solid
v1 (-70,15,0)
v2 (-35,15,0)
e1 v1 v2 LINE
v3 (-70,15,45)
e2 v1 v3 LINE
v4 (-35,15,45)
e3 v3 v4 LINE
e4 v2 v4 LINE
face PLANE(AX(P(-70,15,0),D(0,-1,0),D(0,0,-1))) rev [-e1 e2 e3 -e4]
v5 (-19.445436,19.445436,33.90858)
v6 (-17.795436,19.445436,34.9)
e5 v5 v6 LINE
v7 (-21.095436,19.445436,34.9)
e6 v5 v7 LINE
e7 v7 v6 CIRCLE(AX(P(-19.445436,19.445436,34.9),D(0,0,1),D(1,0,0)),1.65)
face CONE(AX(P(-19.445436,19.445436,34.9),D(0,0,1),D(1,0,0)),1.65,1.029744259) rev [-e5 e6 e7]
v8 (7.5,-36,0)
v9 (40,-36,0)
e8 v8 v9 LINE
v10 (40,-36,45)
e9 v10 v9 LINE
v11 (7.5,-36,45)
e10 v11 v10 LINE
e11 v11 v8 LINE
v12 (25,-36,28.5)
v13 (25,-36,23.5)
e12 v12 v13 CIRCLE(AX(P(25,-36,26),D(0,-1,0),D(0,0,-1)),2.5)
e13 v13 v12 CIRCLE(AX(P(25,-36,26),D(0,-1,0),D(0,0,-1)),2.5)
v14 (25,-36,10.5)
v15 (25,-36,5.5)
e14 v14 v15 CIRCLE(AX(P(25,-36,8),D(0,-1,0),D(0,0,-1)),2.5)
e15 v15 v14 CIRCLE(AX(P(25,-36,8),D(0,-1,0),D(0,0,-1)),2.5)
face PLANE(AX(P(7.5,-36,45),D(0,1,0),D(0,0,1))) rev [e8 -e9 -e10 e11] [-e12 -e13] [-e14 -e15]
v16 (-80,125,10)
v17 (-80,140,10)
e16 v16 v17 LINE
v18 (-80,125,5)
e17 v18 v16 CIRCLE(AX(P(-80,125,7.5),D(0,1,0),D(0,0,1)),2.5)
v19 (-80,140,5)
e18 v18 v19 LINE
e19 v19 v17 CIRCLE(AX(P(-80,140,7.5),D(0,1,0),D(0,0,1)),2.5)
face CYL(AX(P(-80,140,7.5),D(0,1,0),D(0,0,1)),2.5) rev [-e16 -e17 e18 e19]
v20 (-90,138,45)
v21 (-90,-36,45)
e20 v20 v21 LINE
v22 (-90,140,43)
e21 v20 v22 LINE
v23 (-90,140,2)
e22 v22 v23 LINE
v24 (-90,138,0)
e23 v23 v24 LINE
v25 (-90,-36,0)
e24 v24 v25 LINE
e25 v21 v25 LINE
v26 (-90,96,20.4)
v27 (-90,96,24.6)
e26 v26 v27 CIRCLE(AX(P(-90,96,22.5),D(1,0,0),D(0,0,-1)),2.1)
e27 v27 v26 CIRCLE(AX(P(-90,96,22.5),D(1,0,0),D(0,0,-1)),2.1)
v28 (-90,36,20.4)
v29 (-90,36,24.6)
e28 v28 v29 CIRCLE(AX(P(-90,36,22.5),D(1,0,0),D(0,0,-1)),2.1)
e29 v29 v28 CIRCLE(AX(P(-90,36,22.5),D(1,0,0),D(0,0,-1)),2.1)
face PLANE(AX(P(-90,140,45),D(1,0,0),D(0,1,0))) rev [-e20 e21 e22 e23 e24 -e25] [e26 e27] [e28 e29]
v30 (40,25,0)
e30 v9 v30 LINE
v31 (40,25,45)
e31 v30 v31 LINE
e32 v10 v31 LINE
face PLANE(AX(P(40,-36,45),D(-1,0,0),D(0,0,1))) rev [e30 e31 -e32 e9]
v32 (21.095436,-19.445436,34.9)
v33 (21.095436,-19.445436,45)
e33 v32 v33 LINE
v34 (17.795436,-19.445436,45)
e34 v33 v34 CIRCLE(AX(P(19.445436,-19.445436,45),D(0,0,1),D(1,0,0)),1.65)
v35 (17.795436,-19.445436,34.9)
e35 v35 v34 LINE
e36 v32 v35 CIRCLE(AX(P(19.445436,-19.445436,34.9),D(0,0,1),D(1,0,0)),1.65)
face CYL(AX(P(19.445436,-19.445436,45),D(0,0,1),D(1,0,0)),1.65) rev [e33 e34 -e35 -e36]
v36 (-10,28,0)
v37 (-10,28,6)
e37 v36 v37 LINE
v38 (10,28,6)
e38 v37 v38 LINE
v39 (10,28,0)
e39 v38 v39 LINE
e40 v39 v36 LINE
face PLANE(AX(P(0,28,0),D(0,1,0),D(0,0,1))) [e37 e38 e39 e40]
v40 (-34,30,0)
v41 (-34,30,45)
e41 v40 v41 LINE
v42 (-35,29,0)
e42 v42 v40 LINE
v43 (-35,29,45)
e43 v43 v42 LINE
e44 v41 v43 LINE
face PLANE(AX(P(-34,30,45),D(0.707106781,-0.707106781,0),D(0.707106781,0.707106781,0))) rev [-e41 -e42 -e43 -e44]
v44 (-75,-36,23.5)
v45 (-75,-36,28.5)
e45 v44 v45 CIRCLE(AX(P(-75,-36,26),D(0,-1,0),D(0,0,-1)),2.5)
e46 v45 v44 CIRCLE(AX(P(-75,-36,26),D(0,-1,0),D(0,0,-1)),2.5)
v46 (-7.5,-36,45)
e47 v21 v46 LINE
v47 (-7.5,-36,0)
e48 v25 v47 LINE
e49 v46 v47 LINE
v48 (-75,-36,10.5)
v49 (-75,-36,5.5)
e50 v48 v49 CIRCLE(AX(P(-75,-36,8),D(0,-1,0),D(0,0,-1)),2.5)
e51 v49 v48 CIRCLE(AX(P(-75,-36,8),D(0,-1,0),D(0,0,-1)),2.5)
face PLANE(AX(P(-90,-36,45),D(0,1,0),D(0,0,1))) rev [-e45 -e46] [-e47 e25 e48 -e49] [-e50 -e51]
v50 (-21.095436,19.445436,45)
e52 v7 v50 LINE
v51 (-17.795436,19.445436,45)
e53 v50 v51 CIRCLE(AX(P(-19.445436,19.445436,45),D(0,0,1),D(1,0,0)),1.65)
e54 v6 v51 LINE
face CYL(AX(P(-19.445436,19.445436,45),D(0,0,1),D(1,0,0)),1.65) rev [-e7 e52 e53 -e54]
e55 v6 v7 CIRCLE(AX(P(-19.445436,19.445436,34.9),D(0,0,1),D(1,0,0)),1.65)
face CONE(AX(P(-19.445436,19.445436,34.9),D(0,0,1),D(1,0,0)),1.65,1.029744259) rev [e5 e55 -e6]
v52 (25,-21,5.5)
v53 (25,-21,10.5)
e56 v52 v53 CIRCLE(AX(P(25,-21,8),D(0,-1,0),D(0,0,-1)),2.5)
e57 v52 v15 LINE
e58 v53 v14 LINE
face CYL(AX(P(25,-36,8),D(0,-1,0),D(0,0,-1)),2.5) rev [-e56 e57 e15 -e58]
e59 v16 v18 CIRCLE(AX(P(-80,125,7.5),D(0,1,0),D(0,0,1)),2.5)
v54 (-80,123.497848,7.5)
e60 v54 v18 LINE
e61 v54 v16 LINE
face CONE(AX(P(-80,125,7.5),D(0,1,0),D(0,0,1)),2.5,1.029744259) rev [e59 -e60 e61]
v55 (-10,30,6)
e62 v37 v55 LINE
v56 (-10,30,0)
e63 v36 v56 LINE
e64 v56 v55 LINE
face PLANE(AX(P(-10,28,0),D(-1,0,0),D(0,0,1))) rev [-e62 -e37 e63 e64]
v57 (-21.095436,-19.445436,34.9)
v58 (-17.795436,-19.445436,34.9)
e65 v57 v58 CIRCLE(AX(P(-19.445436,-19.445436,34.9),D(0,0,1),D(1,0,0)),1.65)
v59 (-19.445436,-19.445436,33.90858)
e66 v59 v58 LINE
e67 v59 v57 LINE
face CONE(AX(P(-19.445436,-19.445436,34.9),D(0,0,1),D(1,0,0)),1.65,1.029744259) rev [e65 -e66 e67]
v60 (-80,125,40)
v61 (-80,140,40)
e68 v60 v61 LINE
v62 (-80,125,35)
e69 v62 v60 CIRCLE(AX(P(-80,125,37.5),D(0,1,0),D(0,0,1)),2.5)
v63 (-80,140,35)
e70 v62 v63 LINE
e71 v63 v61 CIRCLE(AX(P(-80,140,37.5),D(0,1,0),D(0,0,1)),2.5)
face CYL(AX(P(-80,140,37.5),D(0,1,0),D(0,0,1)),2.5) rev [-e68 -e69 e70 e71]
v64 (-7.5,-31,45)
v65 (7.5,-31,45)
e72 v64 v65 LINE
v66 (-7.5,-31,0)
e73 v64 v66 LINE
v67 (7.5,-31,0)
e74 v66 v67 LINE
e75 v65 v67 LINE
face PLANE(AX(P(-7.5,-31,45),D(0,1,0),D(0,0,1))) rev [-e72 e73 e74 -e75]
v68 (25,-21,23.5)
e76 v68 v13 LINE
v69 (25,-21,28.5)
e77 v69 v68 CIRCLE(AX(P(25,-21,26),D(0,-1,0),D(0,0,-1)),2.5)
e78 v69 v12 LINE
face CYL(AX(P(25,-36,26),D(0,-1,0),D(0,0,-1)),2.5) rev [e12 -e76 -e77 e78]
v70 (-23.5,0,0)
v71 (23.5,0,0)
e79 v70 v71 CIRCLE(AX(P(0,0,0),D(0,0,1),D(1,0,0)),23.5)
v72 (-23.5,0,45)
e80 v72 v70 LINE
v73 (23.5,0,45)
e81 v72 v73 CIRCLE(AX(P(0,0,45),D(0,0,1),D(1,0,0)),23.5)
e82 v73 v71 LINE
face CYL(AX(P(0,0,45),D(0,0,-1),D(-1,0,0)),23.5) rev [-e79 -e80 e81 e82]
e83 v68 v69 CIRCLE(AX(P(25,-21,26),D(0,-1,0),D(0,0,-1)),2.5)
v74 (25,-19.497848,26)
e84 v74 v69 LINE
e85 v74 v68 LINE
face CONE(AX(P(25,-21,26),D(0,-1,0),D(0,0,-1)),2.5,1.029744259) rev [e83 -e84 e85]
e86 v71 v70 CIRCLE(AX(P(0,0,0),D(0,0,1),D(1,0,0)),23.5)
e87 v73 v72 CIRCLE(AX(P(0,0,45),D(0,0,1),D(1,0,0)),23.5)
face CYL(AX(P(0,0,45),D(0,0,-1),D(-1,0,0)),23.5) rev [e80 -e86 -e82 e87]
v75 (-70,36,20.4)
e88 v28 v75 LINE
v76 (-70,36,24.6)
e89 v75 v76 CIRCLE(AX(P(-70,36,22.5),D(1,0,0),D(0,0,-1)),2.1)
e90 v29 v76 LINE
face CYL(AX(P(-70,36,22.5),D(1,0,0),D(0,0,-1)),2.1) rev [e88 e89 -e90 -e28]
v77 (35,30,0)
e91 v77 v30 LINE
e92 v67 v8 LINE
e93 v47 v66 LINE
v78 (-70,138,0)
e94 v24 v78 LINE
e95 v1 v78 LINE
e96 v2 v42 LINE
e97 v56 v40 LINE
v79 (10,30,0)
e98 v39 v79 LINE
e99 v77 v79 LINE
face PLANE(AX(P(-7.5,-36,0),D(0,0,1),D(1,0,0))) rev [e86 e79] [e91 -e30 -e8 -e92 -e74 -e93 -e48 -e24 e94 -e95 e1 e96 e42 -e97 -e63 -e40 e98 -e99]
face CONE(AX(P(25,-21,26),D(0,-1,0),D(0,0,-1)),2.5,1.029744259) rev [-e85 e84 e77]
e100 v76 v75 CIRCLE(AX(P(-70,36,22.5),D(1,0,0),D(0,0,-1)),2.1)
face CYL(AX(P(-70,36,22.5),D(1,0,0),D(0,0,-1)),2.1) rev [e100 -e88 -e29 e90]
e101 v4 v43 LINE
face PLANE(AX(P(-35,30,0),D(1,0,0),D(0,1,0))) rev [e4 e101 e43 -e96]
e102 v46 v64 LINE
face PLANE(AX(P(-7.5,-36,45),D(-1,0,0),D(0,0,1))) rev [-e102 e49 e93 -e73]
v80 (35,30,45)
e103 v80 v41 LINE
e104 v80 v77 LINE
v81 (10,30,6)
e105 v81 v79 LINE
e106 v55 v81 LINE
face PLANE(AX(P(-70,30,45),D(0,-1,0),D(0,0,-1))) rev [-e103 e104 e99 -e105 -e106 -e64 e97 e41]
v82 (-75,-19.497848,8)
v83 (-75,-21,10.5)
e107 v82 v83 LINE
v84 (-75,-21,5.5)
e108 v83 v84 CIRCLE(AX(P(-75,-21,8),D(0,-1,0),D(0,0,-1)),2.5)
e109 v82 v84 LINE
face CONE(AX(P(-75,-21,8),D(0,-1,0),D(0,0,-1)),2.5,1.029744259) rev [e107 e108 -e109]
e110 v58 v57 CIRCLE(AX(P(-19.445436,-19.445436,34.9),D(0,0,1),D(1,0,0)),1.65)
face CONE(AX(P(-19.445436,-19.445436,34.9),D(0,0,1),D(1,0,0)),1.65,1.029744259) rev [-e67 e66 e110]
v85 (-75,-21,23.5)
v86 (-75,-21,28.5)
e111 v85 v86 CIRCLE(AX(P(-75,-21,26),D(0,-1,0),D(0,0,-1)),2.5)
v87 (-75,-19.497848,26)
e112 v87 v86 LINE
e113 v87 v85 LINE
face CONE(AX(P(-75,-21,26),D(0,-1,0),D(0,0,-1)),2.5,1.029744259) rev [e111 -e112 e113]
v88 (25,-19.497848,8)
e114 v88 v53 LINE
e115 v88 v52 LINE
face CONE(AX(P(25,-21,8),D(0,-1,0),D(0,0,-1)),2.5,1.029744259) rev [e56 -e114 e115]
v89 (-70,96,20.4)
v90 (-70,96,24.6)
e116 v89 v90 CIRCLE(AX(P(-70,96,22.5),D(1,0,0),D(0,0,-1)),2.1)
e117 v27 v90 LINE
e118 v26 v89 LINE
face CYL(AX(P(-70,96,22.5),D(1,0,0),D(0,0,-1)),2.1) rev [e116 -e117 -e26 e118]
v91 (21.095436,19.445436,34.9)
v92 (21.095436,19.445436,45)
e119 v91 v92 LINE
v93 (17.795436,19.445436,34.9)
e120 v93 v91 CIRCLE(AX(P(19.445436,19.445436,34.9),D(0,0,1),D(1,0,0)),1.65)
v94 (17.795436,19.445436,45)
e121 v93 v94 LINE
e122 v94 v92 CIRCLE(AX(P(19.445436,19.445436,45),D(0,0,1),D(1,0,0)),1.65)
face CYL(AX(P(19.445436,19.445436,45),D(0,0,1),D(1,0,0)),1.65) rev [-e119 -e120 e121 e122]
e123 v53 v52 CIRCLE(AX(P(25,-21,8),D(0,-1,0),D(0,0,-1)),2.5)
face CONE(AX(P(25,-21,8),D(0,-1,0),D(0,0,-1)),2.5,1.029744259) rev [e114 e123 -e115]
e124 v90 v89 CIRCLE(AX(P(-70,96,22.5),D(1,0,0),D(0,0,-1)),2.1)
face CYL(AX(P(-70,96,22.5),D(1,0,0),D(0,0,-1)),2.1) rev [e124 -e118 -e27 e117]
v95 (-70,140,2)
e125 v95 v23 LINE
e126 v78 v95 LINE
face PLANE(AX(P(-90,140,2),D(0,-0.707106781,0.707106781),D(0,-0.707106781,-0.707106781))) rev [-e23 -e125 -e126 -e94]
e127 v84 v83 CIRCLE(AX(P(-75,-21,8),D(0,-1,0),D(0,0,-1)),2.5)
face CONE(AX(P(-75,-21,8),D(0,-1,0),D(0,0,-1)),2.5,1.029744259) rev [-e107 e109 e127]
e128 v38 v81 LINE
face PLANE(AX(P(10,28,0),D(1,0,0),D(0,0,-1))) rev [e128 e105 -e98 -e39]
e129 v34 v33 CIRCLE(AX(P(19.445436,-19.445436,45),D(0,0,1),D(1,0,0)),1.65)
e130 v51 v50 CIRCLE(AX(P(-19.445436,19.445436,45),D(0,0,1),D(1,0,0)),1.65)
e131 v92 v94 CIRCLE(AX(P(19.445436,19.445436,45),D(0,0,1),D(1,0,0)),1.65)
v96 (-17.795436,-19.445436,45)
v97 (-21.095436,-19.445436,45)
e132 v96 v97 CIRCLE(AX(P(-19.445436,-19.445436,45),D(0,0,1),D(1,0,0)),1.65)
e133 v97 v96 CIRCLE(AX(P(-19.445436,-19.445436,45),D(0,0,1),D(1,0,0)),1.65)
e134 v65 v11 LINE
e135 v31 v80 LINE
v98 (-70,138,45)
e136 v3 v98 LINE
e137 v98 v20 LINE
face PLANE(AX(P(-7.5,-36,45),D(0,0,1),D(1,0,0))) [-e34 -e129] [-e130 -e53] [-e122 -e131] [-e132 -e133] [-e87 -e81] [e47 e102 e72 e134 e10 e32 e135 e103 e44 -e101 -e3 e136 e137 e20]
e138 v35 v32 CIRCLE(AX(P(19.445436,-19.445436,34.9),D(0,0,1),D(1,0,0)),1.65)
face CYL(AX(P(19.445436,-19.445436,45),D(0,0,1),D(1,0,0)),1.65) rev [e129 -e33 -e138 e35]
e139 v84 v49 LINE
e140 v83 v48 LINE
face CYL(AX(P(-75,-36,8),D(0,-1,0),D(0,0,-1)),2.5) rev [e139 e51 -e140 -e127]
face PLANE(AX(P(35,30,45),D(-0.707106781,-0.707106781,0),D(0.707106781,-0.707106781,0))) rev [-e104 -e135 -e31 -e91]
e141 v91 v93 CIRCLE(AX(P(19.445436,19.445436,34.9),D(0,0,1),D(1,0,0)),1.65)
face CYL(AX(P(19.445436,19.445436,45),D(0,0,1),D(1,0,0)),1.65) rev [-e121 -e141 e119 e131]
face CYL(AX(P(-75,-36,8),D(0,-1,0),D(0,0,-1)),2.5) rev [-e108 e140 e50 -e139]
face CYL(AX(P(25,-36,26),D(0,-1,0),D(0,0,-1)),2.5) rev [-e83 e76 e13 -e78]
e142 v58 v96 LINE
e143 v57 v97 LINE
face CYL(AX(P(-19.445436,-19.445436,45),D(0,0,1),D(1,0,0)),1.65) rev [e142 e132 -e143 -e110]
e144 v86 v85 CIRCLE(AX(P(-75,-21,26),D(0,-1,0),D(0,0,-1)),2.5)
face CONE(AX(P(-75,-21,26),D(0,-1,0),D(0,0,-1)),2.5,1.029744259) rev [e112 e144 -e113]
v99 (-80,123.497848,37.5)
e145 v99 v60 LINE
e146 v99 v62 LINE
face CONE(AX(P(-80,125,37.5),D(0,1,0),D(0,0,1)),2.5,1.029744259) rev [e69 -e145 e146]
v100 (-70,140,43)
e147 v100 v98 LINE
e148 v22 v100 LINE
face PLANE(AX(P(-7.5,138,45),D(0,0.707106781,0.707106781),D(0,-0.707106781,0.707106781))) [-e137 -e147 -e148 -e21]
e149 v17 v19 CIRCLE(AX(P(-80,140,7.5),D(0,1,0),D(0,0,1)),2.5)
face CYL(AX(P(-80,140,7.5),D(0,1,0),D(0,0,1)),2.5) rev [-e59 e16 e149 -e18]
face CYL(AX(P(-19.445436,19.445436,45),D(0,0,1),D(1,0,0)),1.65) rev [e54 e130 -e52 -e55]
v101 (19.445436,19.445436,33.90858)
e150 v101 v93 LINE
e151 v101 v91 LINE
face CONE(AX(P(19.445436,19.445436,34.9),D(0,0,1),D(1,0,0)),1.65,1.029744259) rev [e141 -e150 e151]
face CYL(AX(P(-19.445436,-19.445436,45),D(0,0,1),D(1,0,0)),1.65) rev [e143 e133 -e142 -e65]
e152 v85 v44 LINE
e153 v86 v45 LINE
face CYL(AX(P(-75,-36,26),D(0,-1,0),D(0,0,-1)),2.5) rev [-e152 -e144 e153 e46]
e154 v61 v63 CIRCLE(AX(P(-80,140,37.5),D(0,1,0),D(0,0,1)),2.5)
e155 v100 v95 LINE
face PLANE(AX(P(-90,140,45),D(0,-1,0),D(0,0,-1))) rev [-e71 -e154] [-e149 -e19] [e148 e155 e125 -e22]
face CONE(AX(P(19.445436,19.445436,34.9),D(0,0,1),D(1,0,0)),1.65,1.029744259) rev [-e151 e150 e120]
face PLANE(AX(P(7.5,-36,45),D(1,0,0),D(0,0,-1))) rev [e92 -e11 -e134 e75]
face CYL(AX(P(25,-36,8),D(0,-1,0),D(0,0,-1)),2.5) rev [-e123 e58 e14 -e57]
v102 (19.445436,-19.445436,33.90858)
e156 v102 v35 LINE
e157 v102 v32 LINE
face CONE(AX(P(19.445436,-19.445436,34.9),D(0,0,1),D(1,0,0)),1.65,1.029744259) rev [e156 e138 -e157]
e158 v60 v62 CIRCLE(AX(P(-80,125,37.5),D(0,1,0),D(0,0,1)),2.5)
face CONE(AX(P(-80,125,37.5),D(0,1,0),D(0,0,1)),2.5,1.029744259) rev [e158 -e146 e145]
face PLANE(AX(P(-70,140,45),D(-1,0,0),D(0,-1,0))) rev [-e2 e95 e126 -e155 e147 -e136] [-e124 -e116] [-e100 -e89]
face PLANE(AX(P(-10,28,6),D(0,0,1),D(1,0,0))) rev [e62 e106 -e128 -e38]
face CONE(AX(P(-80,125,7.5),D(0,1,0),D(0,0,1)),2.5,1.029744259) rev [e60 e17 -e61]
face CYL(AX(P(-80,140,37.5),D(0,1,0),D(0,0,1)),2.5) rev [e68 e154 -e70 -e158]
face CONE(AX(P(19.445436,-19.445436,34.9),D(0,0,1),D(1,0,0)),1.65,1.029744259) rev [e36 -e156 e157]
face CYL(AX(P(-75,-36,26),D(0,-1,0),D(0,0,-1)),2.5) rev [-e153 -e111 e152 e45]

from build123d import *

# Parameters (mm, degrees)
SKETCH1_R             = 23.5
BOSS_EXTRUDE1_DEPTH   = 45
M6_TAPPED_HOLE1_D     = 5
M6_TAPPED_HOLE1_DEPTH = 15
M6_TAPPED_HOLE1_TIP   = 1.502151548
M5_TAPPED_HOLE1_D     = 4.2
M6_TAPPED_HOLE2_D     = 5
M6_TAPPED_HOLE2_DEPTH = 15
M6_TAPPED_HOLE2_TIP   = 1.502151548
M4_TAPPED_HOLE1_D     = 3.3
M4_TAPPED_HOLE1_DEPTH = 10.1
M4_TAPPED_HOLE1_TIP   = 0.991420021
CHAMFER1_SIZE         = 5
CHAMFER2_SIZE         = 2
SKETCH15_W            = 35
SKETCH15_H            = 15
CUT_EXTRUDE1_DEPTH    = 173.409396496
CHAMFER3_SIZE         = 1
SKETCH18_W            = 20
SKETCH18_H            = 6
CUT_EXTRUDE2_DEPTH    = 2


with BuildPart() as part:
    # Sketch1 → Boss-Extrude1 (new body)
    with BuildSketch(Plane.XY):
        Polygon((-90, 140), (-90, -36), (-7.5, -36), (-7.5, -31), (7.5, -31), (7.5, -36), (40, -36), (40, 30), (-70, 30), (-70, 140), align=None)
        with Locations(Location((0, 0, 0), (0, 0, 180))):
            Circle(SKETCH1_R, mode=Mode.SUBTRACT)
    extrude(amount=BOSS_EXTRUDE1_DEPTH)

    # M6 Tapped Hole1
    with Locations(Plane.XZ.offset(36)):
        with Locations((-75, 8), (25, 8), (-75, 26), (25, 26)):
            Hole(M6_TAPPED_HOLE1_D / 2, depth=M6_TAPPED_HOLE1_DEPTH)
            with Locations((0, 0, -(M6_TAPPED_HOLE1_DEPTH + M6_TAPPED_HOLE1_TIP / 2))):  # 118° drill point
                Cone(0, M6_TAPPED_HOLE1_D / 2, M6_TAPPED_HOLE1_TIP, mode=Mode.SUBTRACT)

    # M5 Tapped Hole1 (through all)
    with Locations(Plane(origin=(-70, 0, 0), x_dir=(0, 0, -1), z_dir=(1, 0, 0))):
        with Locations((-22.5, 96), (-22.5, 36)):
            Hole(M5_TAPPED_HOLE1_D / 2)

    # M6 Tapped Hole2
    with Locations(Plane(origin=(0, 140, 0), x_dir=(-1, 0, 0), z_dir=(0, 1, 0))):
        with Locations((80, 7.5), (80, 37.5)):
            Hole(M6_TAPPED_HOLE2_D / 2, depth=M6_TAPPED_HOLE2_DEPTH)
            with Locations((0, 0, -(M6_TAPPED_HOLE2_DEPTH + M6_TAPPED_HOLE2_TIP / 2))):  # 118° drill point
                Cone(0, M6_TAPPED_HOLE2_D / 2, M6_TAPPED_HOLE2_TIP, mode=Mode.SUBTRACT)

    # M4 Tapped Hole1
    with Locations(Plane.XY.offset(45)):
        with Locations((-19.445436483, -19.445436483), (19.445436483, -19.445436483), (19.445436483, 19.445436483), (-19.445436483, 19.445436483)):
            Hole(M4_TAPPED_HOLE1_D / 2, depth=M4_TAPPED_HOLE1_DEPTH)
            with Locations((0, 0, -(M4_TAPPED_HOLE1_DEPTH + M4_TAPPED_HOLE1_TIP / 2))):  # 118° drill point
                Cone(0, M4_TAPPED_HOLE1_D / 2, M4_TAPPED_HOLE1_TIP, mode=Mode.SUBTRACT)

    # Chamfer1
    chamfer1_edges = [part.edges().sort_by_distance(p)[0] for p in [
        (40, 30, 22.5),
    ]]
    chamfer(chamfer1_edges, length=CHAMFER1_SIZE)

    # Chamfer2
    chamfer2_edges = [part.edges().sort_by_distance(p)[0] for p in [
        (-80, 140, 45),
        (-80, 140, 0),
    ]]
    chamfer(chamfer2_edges, length=CHAMFER2_SIZE)

    # Sketch15 → Cut-Extrude1 (cut, through all)
    with BuildSketch(Plane.XY.offset(45)):
        with Locations((-52.5, 22.5)):
            Rectangle(SKETCH15_W, SKETCH15_H)
    extrude(amount=-CUT_EXTRUDE1_DEPTH, mode=Mode.SUBTRACT)

    # Chamfer3
    chamfer3_edges = [part.edges().sort_by_distance(p)[0] for p in [
        (-35, 30, 22.5),
    ]]
    chamfer(chamfer3_edges, length=CHAMFER3_SIZE)

    # Sketch18 → Cut-Extrude2 (cut)
    with BuildSketch(Plane(origin=(0, 30, 0), x_dir=(1, 0, 0), z_dir=(0, 1, 0))):
        with Locations((0, -3)):
            Rectangle(SKETCH18_W, SKETCH18_H)
    extrude(amount=-CUT_EXTRUDE2_DEPTH, mode=Mode.SUBTRACT)


solid = part.part
